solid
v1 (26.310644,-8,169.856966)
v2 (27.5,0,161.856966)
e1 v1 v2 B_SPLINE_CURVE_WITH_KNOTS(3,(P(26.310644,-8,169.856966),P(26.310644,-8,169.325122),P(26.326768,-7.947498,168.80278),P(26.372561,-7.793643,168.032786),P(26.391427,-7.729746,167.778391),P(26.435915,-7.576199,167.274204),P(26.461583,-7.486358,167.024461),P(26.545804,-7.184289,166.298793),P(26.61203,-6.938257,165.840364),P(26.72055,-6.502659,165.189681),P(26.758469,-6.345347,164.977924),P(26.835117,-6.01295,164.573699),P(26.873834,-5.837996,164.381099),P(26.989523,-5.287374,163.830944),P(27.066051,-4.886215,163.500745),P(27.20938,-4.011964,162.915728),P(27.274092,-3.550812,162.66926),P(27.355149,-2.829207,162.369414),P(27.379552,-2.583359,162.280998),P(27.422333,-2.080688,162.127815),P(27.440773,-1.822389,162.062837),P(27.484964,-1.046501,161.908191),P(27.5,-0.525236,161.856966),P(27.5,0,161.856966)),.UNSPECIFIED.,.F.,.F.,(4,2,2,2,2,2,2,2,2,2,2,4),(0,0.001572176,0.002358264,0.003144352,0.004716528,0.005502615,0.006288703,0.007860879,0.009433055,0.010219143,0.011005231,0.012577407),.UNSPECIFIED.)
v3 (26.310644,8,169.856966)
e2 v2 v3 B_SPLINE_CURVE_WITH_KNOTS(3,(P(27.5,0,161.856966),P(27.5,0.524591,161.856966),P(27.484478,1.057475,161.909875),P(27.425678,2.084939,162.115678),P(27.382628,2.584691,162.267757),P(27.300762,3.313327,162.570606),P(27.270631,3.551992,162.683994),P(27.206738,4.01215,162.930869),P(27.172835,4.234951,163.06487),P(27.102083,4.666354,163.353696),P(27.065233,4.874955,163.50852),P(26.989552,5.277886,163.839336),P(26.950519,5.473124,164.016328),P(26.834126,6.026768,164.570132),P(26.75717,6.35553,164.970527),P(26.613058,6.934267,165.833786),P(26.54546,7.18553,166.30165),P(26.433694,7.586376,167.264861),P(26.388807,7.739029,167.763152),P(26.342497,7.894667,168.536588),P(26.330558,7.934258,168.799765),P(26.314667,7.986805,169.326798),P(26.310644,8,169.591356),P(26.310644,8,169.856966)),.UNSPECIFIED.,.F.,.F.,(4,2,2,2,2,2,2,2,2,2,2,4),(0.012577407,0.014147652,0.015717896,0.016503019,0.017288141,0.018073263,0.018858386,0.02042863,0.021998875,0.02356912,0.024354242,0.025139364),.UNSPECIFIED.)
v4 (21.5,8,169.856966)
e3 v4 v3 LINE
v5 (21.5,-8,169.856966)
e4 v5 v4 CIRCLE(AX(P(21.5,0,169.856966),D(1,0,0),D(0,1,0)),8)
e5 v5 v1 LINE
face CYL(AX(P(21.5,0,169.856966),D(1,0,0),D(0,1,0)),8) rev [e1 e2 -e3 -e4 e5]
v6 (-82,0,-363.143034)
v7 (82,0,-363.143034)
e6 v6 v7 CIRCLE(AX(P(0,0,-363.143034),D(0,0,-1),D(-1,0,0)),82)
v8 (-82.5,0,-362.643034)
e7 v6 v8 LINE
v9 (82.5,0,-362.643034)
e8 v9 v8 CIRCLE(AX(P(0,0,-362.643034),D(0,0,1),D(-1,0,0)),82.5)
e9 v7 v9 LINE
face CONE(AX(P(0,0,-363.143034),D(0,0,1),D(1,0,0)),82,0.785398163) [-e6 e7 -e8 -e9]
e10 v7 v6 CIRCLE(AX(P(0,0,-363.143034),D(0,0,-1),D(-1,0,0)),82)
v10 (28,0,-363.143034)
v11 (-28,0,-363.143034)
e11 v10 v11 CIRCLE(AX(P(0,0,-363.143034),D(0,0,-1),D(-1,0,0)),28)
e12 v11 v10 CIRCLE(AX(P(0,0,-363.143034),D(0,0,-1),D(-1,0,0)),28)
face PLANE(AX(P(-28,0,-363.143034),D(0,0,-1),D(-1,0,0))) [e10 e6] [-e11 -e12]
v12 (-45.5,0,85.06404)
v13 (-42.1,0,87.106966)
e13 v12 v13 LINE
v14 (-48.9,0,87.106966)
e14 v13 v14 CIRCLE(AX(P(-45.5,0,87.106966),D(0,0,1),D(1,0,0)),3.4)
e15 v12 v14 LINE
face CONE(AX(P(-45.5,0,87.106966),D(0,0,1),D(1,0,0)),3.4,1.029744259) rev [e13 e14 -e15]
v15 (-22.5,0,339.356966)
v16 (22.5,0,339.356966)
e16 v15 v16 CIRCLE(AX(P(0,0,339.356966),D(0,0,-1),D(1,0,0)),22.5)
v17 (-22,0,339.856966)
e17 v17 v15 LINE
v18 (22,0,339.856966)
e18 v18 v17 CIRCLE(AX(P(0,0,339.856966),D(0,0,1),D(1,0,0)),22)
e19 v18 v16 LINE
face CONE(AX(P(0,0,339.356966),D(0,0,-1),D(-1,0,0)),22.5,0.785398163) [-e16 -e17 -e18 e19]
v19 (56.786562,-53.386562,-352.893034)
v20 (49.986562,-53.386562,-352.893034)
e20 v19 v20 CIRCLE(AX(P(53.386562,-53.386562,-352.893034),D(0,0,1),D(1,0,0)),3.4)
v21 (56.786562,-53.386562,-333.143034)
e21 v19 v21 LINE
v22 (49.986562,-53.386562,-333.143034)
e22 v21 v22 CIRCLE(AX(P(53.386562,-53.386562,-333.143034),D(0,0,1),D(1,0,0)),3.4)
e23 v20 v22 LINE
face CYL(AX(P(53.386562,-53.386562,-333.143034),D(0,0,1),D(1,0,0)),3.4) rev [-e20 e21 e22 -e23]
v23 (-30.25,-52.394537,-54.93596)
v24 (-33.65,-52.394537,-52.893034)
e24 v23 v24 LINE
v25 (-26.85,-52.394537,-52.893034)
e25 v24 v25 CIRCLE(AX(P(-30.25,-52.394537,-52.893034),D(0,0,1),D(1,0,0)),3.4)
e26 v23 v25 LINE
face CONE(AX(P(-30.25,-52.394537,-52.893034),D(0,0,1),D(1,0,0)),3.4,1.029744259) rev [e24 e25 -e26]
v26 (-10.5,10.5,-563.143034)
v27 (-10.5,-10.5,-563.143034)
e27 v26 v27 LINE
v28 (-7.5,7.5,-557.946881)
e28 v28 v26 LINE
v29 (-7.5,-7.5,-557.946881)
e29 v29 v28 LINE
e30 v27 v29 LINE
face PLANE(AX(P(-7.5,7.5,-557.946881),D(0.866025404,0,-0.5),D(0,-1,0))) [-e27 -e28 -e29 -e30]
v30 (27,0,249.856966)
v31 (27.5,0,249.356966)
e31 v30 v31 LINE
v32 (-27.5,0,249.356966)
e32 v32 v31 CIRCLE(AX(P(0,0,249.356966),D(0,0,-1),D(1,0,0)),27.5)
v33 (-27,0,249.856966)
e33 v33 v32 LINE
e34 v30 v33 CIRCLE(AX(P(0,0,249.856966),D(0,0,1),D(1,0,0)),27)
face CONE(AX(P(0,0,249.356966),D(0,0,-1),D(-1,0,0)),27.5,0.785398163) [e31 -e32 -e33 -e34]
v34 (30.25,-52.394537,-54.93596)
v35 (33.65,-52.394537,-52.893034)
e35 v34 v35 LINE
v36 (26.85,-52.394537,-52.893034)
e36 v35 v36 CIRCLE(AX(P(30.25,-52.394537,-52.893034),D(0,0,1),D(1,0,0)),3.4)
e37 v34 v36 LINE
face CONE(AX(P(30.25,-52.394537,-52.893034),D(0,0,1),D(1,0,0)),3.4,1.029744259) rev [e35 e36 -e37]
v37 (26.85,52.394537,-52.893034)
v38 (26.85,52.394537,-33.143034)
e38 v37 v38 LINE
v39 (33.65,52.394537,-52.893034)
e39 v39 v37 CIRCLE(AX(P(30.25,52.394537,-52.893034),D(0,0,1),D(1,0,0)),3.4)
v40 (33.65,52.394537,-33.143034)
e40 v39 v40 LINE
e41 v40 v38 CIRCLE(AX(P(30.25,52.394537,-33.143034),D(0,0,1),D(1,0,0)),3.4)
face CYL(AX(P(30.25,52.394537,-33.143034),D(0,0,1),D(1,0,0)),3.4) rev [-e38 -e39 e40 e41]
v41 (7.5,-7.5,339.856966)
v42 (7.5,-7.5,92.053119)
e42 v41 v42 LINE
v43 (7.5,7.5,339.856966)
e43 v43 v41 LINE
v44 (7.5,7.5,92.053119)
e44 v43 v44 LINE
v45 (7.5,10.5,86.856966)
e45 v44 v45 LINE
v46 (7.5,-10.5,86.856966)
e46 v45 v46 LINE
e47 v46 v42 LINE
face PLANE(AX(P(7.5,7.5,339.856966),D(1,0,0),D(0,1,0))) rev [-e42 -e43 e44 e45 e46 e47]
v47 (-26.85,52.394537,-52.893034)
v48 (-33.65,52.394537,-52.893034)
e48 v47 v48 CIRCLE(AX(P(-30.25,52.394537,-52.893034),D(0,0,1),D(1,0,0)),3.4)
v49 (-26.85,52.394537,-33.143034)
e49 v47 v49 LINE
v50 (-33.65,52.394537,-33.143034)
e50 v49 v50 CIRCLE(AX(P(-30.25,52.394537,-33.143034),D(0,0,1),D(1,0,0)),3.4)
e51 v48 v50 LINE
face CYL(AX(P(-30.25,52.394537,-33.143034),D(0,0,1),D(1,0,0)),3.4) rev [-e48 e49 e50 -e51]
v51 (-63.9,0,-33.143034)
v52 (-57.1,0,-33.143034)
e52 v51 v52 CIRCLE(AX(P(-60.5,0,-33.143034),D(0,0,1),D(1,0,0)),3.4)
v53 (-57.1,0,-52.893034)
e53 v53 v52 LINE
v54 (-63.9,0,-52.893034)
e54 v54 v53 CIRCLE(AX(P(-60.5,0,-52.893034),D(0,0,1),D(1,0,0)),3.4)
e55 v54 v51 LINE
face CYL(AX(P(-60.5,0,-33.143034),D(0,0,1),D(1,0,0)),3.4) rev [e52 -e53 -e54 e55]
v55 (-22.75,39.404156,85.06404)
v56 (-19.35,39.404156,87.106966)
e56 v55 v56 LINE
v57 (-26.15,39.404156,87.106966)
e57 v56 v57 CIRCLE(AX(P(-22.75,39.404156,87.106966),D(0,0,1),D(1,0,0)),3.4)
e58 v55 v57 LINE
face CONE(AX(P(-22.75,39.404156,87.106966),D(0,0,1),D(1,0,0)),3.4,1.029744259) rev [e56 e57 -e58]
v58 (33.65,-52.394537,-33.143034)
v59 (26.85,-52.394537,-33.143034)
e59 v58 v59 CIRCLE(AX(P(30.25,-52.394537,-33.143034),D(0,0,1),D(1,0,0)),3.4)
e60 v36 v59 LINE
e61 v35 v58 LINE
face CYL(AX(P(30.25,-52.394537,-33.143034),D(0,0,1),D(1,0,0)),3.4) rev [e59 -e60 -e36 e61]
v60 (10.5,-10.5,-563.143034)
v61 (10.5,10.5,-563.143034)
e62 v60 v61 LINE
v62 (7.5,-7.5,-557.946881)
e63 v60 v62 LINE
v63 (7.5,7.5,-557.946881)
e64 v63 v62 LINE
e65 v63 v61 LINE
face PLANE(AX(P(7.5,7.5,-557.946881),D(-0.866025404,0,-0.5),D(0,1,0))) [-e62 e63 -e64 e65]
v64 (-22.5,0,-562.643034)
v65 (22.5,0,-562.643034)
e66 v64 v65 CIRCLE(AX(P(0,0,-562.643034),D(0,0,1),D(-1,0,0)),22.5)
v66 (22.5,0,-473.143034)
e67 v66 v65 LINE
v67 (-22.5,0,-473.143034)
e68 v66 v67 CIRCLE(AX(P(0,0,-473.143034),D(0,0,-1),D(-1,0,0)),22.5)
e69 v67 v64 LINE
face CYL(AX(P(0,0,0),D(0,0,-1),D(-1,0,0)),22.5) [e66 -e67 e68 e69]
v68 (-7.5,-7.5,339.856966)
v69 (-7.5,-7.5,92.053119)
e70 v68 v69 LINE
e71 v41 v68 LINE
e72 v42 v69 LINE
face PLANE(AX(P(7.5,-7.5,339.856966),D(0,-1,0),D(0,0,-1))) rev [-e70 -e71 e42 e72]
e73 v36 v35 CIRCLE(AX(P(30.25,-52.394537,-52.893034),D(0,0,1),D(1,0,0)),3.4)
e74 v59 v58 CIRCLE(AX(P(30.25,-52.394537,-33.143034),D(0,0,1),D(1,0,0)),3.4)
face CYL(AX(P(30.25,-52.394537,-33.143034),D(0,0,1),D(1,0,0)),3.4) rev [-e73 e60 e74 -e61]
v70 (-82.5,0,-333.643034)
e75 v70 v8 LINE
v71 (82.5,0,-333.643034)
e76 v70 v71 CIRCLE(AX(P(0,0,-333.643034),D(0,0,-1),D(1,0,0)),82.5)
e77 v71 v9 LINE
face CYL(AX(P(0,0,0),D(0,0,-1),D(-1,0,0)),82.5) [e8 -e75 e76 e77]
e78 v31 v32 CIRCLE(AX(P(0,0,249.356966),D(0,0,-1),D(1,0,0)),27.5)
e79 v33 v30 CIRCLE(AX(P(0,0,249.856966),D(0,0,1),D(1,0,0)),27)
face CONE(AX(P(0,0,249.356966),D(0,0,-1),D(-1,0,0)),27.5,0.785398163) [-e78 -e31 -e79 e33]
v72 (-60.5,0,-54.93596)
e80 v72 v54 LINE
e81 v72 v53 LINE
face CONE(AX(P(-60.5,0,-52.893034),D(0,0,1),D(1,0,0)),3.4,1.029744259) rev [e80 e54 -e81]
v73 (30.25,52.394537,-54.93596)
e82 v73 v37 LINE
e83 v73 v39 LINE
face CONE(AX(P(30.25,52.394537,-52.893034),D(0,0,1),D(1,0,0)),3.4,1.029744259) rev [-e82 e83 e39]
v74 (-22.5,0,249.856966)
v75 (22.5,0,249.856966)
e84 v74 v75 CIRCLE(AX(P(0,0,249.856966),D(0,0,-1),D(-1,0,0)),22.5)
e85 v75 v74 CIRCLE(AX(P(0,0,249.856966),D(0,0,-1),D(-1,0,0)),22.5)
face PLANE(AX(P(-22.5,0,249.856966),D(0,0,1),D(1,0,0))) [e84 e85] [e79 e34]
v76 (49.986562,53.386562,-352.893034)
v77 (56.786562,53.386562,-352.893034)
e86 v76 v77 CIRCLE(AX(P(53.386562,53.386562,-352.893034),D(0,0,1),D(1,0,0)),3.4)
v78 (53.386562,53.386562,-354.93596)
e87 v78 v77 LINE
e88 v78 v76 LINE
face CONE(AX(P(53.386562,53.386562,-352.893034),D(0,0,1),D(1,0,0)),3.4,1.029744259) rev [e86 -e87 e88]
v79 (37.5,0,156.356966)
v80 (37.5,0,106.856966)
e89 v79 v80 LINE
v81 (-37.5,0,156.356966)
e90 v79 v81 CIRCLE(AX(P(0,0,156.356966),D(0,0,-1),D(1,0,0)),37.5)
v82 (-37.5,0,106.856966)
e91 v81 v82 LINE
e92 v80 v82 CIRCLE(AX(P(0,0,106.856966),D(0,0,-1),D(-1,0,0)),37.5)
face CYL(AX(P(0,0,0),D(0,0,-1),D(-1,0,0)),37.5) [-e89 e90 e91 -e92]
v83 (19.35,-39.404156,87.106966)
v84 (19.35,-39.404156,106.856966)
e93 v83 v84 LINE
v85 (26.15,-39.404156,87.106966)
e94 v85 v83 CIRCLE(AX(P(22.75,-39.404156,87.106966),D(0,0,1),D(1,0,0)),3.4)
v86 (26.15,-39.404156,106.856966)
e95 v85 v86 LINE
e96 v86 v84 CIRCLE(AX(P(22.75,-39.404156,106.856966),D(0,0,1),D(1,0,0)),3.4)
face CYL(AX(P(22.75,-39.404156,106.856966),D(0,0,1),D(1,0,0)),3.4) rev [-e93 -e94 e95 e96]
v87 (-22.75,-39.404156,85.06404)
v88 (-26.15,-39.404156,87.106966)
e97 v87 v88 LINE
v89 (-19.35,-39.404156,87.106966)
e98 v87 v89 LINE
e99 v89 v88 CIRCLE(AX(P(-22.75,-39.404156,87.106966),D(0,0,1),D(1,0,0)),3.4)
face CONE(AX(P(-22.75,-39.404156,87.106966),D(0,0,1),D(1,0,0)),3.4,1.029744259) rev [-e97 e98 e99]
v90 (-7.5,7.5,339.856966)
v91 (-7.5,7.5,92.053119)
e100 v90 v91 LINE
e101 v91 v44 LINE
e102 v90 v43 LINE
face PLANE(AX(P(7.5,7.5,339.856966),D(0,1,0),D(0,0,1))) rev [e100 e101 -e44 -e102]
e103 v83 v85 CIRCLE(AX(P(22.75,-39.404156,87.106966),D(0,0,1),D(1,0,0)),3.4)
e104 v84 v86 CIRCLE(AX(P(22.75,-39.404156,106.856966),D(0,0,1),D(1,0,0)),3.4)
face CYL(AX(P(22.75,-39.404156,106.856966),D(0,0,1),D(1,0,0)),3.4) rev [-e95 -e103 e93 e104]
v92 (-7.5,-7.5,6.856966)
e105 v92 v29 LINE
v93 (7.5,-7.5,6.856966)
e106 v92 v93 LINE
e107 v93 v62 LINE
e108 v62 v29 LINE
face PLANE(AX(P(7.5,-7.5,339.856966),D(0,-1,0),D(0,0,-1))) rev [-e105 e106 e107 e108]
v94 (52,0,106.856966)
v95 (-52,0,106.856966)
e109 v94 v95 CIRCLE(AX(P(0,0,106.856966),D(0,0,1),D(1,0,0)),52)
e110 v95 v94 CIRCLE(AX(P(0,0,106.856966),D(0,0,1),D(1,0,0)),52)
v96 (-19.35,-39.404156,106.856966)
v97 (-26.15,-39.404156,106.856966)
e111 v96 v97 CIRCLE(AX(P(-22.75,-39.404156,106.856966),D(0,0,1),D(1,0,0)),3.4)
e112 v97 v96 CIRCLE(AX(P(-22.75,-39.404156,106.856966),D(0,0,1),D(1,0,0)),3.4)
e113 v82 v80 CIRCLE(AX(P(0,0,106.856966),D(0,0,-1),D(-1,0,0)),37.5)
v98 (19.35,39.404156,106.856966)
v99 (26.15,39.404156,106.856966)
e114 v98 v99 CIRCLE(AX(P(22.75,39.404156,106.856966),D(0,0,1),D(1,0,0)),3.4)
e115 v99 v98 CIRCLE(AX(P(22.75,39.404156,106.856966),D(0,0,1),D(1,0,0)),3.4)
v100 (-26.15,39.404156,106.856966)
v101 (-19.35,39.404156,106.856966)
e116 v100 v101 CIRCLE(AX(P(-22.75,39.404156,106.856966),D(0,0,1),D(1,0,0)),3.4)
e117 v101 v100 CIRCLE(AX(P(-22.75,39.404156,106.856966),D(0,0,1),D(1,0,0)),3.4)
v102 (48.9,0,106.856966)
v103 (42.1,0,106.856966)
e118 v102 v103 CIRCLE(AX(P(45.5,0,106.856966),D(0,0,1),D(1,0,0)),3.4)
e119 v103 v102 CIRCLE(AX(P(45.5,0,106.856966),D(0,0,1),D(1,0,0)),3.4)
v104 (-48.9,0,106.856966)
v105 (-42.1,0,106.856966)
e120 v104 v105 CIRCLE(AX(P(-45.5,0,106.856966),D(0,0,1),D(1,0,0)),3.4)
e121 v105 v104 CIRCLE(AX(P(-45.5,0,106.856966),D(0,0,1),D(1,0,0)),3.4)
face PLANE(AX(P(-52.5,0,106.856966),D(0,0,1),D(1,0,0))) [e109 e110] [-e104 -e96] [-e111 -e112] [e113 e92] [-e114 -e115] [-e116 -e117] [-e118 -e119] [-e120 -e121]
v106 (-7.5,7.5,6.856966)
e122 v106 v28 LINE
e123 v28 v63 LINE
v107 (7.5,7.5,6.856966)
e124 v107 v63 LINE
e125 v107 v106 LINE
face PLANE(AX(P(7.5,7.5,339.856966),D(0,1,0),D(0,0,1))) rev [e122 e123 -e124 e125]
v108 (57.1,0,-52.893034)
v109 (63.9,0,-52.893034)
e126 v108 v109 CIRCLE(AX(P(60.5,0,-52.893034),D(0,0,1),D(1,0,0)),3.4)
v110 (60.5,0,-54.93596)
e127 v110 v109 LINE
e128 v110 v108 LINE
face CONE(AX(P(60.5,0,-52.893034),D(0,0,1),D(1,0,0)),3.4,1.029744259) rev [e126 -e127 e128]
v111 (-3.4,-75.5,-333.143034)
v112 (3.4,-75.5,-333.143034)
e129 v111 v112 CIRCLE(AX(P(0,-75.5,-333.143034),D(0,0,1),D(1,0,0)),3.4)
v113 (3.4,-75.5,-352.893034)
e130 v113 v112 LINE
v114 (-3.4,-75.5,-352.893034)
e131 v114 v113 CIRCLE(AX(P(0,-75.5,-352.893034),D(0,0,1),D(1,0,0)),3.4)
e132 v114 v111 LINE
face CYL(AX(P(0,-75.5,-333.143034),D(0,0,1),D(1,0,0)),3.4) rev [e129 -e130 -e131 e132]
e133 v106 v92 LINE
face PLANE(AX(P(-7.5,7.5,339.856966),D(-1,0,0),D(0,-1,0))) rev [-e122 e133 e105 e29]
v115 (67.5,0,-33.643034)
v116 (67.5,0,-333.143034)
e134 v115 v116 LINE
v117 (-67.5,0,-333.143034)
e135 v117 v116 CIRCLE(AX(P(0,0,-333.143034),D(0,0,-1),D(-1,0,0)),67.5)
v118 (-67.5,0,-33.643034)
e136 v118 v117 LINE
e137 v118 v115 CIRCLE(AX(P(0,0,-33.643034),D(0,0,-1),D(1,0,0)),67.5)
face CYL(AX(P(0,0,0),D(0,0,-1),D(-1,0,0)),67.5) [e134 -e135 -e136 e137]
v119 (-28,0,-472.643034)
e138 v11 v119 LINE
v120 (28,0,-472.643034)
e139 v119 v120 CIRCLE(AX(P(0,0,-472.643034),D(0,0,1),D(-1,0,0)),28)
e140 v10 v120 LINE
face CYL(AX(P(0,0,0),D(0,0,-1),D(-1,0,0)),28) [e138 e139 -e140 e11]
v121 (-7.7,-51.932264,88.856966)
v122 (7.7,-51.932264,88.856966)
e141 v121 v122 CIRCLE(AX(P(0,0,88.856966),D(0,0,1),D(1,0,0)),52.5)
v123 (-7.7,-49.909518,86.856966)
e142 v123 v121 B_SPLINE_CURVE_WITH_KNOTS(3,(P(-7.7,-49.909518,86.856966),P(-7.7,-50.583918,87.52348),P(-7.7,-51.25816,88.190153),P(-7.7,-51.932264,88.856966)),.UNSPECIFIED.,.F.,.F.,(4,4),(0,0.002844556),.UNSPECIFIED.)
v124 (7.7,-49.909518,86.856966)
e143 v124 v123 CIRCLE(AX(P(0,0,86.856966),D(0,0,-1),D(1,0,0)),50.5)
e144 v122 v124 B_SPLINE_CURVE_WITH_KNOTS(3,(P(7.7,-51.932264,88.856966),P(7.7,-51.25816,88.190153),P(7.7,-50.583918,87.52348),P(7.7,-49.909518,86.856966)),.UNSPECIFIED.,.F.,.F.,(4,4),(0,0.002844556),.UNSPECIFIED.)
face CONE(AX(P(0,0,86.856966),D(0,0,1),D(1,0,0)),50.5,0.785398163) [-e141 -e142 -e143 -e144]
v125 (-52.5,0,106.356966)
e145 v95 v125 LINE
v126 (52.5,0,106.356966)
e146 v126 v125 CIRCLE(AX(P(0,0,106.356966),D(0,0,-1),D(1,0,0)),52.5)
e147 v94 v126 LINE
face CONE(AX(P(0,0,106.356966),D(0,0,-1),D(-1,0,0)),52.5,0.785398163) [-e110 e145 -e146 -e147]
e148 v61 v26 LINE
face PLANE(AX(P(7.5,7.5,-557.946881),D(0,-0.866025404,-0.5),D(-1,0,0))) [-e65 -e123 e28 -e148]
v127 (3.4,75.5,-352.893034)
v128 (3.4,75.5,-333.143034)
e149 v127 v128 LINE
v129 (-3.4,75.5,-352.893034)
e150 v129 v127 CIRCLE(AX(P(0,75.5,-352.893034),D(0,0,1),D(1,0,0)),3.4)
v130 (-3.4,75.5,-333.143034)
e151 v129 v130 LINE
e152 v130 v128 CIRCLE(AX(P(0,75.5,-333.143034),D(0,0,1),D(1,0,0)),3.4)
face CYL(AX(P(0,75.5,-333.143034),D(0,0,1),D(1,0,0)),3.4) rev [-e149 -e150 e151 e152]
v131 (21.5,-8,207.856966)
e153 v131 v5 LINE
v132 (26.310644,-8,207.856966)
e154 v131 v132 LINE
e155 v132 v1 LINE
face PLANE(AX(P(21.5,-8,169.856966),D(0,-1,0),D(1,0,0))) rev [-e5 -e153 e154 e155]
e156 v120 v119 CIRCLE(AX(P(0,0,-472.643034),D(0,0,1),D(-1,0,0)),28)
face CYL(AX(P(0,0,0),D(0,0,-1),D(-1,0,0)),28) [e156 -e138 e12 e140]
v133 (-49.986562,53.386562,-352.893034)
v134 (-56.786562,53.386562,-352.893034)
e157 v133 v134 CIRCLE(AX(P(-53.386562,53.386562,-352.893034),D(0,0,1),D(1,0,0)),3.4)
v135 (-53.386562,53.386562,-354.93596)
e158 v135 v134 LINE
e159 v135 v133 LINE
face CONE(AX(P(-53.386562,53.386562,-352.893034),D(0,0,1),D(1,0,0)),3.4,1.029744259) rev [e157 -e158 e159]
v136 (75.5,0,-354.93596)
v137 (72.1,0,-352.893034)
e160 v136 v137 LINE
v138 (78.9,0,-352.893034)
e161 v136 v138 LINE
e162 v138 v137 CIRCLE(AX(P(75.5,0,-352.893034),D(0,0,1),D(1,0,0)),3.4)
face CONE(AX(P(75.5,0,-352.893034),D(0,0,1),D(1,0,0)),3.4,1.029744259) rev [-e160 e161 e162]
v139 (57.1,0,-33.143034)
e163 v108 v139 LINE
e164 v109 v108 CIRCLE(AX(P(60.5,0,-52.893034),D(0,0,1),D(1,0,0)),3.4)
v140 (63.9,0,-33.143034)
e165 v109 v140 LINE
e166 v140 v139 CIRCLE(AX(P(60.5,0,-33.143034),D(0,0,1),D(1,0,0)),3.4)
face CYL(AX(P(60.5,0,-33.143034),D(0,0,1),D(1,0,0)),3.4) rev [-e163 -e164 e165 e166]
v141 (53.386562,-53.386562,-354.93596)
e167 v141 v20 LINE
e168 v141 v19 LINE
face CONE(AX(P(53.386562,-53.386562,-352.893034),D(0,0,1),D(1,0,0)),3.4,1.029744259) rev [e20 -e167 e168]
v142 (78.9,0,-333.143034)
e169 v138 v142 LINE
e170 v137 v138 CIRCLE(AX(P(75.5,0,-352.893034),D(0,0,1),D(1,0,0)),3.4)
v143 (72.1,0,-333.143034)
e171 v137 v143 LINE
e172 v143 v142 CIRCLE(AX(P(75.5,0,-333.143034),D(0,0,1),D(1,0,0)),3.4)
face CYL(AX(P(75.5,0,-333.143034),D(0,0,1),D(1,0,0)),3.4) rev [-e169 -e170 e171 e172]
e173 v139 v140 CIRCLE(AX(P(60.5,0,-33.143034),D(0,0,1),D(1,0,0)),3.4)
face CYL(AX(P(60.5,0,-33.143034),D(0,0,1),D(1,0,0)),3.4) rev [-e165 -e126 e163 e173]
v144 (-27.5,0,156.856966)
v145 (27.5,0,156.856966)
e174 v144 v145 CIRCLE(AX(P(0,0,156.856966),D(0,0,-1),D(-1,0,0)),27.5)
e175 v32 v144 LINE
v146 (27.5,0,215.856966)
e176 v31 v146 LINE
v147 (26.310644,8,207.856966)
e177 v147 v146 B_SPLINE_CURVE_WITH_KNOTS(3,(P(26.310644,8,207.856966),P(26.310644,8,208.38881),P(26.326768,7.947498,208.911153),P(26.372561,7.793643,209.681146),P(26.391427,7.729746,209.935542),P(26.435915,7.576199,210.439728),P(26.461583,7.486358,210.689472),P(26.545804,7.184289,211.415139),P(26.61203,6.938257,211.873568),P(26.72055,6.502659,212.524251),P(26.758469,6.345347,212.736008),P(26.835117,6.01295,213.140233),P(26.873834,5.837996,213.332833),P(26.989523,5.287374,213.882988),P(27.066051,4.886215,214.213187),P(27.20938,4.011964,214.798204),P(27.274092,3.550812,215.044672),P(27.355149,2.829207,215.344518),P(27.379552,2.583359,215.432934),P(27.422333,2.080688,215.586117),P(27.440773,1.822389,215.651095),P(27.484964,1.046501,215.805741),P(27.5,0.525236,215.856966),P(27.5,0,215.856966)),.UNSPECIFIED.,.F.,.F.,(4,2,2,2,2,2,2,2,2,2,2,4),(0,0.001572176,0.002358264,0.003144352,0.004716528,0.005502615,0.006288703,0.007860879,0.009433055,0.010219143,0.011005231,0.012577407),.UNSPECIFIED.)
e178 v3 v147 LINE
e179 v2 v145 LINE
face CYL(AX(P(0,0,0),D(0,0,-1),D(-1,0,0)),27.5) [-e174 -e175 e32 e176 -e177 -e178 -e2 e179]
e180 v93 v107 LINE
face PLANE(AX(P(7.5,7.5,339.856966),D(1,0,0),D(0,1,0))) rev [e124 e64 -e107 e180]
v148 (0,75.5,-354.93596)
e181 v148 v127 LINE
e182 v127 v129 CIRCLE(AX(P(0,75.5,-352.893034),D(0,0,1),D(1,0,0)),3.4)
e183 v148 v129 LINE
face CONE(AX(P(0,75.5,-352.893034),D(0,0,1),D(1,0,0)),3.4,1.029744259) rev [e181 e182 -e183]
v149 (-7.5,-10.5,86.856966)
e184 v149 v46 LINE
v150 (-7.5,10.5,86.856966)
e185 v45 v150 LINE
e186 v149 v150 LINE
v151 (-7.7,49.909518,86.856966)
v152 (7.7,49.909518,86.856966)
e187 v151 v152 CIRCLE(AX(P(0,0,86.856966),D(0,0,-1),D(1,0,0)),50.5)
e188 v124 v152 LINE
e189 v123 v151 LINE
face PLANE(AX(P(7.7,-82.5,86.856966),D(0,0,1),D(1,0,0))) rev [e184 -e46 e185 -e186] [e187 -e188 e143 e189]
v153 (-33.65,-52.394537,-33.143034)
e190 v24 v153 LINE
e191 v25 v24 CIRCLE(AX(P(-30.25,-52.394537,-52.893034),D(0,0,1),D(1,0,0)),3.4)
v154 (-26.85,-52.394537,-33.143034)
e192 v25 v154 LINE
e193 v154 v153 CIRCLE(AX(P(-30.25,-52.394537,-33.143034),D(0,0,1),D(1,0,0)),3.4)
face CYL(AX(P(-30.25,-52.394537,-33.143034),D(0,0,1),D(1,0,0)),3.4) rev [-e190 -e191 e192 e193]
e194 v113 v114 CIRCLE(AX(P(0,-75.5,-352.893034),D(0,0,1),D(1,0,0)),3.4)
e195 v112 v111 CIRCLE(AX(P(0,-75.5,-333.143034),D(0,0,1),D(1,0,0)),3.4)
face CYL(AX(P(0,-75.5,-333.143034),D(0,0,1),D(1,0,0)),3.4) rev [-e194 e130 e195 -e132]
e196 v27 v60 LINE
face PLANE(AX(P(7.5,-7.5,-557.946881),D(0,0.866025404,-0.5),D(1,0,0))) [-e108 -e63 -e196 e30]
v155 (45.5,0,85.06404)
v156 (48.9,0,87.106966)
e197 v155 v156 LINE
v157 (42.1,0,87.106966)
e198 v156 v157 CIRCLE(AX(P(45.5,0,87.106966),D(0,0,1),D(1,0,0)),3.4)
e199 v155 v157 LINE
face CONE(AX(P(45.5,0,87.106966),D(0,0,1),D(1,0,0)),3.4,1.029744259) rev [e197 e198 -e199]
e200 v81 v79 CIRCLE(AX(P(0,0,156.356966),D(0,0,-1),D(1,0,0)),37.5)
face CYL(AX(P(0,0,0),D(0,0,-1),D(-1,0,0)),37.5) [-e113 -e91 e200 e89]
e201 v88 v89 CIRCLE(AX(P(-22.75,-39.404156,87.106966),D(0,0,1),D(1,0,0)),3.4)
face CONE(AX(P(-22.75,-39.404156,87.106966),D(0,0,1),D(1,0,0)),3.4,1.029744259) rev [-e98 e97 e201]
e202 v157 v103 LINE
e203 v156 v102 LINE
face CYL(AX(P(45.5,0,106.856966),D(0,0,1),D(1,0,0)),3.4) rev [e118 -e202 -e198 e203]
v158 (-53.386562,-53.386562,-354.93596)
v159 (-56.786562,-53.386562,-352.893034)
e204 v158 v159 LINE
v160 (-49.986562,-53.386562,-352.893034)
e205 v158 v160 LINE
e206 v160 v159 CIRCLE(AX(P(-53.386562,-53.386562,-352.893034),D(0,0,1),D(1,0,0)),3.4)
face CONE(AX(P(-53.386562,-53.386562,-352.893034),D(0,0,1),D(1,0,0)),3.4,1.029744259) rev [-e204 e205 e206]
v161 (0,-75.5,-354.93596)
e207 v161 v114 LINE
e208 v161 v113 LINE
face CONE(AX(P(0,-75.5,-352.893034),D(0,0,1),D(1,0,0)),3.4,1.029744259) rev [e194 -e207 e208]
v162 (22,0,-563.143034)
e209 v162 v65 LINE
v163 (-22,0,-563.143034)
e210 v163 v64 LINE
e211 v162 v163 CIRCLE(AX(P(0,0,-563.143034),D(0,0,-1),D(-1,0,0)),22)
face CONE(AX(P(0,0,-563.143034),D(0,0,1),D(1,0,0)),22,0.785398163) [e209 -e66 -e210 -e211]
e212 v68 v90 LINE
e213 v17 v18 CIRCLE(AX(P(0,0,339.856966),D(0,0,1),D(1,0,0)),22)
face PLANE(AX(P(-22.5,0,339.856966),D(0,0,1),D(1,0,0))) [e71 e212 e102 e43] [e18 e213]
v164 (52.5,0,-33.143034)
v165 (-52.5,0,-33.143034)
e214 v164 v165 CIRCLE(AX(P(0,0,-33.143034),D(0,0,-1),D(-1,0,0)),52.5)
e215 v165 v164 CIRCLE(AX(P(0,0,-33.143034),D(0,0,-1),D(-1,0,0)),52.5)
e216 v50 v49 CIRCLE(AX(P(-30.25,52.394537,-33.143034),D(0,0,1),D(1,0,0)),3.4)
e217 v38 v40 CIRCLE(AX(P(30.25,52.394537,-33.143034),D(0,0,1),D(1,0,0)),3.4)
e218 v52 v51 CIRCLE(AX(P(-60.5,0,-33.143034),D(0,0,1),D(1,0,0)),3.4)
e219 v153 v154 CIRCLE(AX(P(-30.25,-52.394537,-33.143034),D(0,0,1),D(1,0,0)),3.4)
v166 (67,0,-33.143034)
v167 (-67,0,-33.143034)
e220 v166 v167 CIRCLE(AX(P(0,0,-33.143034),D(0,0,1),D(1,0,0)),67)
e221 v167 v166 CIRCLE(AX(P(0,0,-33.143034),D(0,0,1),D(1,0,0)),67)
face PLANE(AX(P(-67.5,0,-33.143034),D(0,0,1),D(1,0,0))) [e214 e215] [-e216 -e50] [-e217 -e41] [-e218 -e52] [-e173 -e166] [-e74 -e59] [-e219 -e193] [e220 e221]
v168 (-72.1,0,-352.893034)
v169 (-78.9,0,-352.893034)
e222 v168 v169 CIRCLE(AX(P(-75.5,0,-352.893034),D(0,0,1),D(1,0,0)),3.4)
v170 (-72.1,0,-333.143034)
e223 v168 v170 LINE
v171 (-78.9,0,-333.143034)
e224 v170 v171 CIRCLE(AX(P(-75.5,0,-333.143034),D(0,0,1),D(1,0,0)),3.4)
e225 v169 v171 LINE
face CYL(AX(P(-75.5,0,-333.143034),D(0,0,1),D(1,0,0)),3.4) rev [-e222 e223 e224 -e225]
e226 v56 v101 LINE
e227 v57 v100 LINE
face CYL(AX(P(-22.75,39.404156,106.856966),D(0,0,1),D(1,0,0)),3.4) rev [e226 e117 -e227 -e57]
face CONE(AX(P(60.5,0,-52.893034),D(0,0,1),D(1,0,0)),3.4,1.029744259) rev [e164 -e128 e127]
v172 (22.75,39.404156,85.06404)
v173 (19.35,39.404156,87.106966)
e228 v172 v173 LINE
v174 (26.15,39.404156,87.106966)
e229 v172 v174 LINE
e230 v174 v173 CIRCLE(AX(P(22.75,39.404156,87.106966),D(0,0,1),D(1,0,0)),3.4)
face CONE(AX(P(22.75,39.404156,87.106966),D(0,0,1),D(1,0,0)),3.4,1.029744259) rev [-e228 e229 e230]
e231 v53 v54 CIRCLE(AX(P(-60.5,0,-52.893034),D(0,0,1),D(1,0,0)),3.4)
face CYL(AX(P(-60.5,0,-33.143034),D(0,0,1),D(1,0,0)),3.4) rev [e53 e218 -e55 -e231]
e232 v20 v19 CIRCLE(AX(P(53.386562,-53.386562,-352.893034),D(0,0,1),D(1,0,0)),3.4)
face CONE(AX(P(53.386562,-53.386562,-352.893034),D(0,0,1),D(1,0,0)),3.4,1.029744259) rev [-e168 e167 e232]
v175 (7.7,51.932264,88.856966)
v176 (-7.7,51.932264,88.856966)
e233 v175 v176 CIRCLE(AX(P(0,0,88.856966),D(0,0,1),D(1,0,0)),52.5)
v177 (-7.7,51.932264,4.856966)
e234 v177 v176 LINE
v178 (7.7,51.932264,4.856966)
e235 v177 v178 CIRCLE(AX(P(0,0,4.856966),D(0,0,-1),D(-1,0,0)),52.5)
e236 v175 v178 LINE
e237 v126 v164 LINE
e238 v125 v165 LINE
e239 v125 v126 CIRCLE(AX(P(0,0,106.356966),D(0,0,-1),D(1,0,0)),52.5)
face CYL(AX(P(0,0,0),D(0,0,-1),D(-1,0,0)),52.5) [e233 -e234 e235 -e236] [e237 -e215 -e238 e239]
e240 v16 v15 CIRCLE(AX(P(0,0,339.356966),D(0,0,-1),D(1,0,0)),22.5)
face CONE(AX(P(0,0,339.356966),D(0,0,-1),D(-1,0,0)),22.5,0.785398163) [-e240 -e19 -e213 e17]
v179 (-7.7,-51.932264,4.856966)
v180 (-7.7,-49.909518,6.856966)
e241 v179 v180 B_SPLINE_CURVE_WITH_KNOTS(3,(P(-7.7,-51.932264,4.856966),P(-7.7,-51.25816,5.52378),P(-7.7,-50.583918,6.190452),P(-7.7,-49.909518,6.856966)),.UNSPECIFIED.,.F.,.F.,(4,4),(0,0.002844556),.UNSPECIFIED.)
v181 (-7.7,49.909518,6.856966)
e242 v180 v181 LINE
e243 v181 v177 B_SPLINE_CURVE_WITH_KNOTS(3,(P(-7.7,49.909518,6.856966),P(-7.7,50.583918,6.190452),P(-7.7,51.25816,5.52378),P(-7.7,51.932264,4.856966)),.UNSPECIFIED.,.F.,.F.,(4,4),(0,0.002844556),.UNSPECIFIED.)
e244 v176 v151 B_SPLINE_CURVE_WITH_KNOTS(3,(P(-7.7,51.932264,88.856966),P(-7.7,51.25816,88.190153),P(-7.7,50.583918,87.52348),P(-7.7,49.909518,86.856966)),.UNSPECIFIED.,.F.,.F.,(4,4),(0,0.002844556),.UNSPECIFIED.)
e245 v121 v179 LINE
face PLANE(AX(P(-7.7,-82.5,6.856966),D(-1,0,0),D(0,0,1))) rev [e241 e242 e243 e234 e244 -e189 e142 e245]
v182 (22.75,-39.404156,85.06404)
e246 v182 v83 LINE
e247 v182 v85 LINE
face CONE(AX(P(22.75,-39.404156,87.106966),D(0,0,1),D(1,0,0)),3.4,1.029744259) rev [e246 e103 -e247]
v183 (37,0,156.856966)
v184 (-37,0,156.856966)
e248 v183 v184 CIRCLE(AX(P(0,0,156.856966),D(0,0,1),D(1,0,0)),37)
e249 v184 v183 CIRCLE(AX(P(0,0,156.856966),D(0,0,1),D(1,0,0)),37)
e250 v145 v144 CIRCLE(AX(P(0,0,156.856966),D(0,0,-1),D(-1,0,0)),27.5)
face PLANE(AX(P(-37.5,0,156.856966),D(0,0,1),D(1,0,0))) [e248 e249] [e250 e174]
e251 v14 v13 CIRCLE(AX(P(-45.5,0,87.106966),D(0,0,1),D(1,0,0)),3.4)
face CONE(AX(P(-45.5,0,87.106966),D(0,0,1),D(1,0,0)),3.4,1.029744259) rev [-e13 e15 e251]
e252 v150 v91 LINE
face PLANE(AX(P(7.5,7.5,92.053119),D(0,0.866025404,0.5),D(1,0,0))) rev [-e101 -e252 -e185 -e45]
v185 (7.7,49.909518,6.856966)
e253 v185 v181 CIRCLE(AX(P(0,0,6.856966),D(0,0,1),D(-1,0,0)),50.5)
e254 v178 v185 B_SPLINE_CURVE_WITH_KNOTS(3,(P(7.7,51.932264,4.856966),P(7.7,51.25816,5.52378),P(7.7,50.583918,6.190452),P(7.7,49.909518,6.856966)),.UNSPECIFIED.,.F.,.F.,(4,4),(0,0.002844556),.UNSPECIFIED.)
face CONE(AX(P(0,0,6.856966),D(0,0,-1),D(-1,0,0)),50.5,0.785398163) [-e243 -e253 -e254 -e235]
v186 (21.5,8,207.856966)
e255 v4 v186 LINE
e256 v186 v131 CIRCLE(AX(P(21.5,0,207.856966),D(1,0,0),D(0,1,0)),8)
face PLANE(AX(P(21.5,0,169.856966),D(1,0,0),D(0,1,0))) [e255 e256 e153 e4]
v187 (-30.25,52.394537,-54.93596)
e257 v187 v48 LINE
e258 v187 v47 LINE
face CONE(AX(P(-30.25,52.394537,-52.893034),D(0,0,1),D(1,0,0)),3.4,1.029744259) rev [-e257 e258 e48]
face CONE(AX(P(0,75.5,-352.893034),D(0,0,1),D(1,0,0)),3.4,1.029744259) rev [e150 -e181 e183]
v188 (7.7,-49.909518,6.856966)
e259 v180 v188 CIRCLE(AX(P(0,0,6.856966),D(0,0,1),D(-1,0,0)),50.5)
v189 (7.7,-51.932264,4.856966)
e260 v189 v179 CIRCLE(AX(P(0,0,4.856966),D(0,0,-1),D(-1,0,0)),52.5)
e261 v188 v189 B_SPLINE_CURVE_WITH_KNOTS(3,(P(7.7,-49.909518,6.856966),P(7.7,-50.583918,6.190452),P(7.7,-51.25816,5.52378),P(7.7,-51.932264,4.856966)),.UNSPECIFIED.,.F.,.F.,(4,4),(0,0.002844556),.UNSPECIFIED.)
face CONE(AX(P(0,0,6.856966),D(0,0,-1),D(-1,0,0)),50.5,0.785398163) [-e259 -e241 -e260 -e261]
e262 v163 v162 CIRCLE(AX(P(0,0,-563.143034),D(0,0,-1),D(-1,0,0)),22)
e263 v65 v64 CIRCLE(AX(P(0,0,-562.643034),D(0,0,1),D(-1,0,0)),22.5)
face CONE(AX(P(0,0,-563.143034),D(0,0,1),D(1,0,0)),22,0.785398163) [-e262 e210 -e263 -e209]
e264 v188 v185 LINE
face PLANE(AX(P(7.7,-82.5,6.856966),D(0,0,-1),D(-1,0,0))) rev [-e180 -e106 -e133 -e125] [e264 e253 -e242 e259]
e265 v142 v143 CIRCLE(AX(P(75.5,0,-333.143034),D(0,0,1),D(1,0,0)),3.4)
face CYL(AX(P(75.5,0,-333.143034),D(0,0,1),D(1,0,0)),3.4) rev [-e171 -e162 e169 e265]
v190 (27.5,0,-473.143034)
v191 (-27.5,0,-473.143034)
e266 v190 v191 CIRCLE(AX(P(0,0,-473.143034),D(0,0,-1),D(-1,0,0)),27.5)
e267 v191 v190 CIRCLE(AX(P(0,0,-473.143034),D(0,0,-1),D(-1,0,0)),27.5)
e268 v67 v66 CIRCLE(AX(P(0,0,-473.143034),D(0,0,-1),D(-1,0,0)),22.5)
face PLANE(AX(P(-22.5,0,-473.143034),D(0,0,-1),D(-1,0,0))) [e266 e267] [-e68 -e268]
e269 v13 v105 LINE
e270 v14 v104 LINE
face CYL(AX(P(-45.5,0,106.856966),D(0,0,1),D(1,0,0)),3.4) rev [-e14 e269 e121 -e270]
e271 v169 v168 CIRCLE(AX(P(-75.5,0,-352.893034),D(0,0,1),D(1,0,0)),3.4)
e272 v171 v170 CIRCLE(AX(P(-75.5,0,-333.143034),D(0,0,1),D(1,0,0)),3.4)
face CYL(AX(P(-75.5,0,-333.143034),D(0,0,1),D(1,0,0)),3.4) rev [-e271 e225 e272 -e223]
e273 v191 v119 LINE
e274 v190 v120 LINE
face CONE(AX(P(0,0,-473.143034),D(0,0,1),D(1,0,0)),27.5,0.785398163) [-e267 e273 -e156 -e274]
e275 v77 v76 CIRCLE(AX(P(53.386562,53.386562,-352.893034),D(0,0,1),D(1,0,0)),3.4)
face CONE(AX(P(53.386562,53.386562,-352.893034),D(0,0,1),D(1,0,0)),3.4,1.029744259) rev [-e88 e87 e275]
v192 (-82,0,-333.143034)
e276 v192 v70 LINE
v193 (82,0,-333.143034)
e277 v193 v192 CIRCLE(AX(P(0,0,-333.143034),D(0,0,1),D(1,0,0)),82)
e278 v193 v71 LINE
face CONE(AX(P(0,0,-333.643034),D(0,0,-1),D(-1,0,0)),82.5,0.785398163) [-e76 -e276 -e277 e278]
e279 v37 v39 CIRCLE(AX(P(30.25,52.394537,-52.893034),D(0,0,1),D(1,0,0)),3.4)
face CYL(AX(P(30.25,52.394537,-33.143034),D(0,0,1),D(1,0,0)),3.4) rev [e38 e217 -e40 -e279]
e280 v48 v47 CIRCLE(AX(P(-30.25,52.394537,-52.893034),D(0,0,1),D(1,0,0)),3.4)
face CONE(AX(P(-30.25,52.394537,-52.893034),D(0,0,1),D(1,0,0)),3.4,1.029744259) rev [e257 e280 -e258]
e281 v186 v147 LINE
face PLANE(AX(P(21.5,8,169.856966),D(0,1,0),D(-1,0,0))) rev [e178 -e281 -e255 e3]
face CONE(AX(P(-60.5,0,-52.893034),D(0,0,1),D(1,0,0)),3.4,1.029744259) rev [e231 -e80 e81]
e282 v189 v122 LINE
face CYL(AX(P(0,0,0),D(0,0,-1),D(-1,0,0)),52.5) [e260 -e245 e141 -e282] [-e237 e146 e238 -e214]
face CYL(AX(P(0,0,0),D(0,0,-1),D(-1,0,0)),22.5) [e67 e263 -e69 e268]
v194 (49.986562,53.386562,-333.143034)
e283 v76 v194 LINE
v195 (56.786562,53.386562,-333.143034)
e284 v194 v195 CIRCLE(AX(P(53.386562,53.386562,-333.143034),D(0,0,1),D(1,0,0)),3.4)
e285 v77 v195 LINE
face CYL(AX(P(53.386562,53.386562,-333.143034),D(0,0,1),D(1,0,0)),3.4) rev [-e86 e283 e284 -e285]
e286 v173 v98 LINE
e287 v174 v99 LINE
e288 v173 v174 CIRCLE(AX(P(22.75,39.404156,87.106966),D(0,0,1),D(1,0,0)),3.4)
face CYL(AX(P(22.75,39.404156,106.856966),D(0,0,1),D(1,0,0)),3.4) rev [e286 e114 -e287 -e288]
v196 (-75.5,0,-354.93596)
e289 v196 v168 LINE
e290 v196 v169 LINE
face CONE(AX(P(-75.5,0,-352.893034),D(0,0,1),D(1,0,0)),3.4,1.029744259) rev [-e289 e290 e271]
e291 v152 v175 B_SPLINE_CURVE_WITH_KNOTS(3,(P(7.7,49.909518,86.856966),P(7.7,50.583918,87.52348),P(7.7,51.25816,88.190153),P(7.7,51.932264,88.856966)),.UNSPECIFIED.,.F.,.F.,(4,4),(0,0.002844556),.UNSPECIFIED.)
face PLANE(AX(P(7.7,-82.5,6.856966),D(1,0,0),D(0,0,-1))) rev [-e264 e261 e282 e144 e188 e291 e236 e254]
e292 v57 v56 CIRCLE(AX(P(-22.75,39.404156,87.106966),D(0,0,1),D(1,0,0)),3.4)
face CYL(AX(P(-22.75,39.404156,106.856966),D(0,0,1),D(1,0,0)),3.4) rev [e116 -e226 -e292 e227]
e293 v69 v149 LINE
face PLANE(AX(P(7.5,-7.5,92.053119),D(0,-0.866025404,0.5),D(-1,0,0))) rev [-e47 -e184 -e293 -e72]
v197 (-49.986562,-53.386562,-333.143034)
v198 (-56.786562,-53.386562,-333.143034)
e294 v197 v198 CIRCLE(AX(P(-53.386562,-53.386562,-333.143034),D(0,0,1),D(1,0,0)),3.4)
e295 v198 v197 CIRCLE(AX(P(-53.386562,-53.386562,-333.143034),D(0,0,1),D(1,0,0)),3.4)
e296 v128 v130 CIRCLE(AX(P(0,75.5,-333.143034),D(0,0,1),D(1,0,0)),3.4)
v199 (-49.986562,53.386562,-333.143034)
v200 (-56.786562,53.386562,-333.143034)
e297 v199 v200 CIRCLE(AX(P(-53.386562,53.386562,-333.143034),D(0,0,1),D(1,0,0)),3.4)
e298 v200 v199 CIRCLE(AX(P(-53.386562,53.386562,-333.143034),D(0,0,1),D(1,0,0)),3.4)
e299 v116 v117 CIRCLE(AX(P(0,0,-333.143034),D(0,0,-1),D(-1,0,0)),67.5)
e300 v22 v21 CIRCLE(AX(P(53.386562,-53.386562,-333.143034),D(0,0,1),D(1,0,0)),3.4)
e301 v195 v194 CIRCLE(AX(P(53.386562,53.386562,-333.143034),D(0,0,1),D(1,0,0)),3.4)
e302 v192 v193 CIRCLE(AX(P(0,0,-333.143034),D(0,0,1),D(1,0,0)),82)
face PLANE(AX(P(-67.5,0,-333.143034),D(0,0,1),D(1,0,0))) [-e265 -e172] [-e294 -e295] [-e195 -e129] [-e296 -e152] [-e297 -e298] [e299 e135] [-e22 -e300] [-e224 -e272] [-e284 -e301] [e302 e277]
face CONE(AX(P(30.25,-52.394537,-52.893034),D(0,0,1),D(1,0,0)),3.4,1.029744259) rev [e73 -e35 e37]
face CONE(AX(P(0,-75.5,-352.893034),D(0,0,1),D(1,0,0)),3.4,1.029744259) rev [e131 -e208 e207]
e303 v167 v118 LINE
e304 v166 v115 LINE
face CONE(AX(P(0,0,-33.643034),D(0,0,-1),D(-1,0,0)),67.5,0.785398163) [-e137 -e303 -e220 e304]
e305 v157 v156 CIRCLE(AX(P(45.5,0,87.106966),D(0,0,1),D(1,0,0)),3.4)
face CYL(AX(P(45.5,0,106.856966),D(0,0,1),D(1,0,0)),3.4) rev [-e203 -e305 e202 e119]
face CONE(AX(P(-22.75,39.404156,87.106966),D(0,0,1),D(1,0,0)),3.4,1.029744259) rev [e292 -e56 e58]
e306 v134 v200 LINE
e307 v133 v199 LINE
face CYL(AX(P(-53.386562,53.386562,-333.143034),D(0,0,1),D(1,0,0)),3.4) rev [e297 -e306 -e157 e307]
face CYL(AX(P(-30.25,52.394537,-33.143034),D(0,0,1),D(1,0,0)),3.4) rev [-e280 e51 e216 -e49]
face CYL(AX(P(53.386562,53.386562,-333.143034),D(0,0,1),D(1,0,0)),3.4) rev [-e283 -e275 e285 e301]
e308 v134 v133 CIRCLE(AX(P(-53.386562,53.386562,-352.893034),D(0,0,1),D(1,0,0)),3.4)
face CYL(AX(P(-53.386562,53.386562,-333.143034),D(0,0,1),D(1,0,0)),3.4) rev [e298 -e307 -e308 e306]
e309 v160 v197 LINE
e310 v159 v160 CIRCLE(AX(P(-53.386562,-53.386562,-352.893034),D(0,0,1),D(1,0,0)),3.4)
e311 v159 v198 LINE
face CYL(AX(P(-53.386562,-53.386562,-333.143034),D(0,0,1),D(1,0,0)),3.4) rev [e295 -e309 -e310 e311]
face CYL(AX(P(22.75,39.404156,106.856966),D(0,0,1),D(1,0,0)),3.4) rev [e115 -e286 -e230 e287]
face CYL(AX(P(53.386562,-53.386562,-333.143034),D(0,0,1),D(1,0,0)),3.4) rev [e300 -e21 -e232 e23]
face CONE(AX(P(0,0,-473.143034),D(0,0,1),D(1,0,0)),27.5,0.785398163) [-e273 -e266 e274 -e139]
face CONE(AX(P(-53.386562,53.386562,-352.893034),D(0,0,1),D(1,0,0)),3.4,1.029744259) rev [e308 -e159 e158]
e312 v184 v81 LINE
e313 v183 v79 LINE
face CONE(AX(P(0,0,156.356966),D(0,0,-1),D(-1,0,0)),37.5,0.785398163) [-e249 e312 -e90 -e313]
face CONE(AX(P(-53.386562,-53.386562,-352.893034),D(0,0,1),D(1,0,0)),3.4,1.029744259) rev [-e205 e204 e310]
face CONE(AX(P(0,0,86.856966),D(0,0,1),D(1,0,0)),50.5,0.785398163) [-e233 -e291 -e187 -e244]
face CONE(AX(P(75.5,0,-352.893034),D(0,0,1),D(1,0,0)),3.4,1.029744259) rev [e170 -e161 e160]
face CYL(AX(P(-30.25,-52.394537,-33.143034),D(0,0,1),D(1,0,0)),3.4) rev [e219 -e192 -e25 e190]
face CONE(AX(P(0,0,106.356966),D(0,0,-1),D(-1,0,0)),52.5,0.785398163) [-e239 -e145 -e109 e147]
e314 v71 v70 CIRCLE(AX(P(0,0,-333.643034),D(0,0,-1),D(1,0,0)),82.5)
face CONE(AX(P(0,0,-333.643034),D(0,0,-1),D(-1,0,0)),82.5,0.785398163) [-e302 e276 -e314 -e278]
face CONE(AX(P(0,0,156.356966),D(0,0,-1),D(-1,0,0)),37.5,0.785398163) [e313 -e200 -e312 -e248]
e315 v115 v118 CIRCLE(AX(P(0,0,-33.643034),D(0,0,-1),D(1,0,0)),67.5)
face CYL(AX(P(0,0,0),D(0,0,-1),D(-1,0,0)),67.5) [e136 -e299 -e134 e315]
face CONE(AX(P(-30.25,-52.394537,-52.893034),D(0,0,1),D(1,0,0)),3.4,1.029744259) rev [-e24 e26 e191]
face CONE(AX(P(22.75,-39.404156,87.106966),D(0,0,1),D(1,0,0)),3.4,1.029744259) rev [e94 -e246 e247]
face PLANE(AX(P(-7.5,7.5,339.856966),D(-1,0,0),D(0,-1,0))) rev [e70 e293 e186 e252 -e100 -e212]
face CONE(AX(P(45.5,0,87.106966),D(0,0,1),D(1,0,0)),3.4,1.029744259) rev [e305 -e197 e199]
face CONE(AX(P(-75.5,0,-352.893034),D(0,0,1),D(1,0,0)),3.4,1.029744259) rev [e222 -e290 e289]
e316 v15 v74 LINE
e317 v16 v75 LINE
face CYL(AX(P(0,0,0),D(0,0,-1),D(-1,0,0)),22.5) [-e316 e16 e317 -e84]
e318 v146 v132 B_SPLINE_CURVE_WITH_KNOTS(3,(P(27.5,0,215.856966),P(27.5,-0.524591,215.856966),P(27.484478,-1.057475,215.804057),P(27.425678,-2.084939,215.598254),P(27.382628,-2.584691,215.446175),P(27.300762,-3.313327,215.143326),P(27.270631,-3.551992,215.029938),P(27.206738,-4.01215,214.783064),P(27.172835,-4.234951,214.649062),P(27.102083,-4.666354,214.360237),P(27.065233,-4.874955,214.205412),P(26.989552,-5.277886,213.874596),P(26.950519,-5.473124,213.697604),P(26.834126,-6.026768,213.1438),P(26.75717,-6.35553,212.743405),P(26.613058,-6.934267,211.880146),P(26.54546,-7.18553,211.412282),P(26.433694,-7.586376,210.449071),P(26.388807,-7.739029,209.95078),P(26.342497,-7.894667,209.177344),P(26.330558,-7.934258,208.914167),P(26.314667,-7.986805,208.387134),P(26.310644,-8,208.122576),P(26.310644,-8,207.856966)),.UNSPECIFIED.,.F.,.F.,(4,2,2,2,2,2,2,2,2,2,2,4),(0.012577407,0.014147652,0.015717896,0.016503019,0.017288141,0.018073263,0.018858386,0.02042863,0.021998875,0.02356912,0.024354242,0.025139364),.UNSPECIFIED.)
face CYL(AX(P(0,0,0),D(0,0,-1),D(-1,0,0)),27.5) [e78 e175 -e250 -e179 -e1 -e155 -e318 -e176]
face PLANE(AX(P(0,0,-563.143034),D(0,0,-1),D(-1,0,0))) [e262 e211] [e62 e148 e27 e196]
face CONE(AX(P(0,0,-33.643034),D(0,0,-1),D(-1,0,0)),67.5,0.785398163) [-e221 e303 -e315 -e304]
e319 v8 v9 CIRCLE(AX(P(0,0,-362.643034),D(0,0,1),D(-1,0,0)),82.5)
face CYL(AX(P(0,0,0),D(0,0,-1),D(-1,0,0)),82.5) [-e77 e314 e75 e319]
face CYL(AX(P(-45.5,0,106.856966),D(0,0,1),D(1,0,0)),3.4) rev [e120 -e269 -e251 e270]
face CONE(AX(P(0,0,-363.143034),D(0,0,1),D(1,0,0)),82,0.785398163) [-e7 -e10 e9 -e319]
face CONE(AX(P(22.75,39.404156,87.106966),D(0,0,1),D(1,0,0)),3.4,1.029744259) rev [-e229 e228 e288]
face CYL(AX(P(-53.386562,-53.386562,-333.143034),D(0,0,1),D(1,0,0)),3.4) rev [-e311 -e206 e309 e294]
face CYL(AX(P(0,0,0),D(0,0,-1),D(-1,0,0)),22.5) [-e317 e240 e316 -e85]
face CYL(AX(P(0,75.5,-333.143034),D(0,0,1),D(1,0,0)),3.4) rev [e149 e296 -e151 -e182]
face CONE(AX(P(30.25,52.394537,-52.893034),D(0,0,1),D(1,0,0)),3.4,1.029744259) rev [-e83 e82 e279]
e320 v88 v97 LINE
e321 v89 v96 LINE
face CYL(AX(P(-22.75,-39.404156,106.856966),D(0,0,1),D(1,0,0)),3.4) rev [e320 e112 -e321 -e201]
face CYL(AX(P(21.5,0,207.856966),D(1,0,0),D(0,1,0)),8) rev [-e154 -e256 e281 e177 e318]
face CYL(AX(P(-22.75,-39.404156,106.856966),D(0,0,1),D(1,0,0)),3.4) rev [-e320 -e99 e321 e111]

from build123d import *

# Parameters (mm, degrees)
SKETCH_3_W               = 15
SKETCH_3_H               = 15
CUT_EXTRUDE_1_DEPTH      = 911.506177903
CUT_EXTRUDE_2_DEPTH      = 576.102231468
CUT_EXTRUDE_2_DEPTH_BACK = 576.102231468
SKETCH_4_W               = 15.4
SKETCH_4_H               = 80
CHAMFER_1_SIZE           = 2
PATTERN_CIRCULAR_1_COUNT = 6
PATTERN_CIRCULAR_2_COUNT = 6
PATTERN_CIRCULAR_3_COUNT = 8
CHAMFER_2_SIZE           = 0.5
CHAMFER_3_SIZE           = 3
CHAMFER_3_SIZE2          = 5.196152423
CHAMFER_4_SIZE           = 3
CHAMFER_4_SIZE2          = 5.196152423
CUT_EXTRUDE_3_DEPTH      = 6


with BuildPart() as part:
    # 草图2 → 旋转1 (revolve)
    with BuildSketch(Plane(origin=(0, 0, 0), x_dir=(1, 0, 0), z_dir=(0, 1, 0))):
        Polygon((0, 563.143033908), (-22.5, 563.143033908), (-22.5, 473.143033908), (-28, 473.143033908), (-28, 363.143033908), (-82.5, 363.143033908), (-82.5, 333.143033908), (-67.5, 333.143033908), (-67.5, 33.143033908), (-52.5, 33.143033908), (-52.5, -106.856966092), (-37.5, -106.856966092), (-37.5, -156.856966092), (-27.5, -156.856966092), (-27.5, -249.856966092), (-22.5, -249.856966092), (-22.5, -339.856966092), (0, -339.856966092), align=None)
    revolve(axis=Axis((0, 0, 0), (0, 0, 1)))

    # 草图3 → 切除-拉伸1 (cut, through all)
    with BuildSketch(Plane(origin=(0, 0, -563.143033908), x_dir=(-1, 0, 0), z_dir=(0, 0, -1))):
        Rectangle(SKETCH_3_W, SKETCH_3_H)
    extrude(amount=-CUT_EXTRUDE_1_DEPTH, mode=Mode.SUBTRACT)

    # 草图4 → 切除-拉伸2 (cut, two sides: drawn at the far end of the back side and taken through both)
    with BuildSketch(Plane(origin=(0, 0, 0), x_dir=(1, 0, 0), z_dir=(0, 1, 0)).offset(-CUT_EXTRUDE_2_DEPTH_BACK)):
        with Locations((0, -46.856966092)):
            Rectangle(SKETCH_4_W, SKETCH_4_H)
    extrude(amount=CUT_EXTRUDE_2_DEPTH + CUT_EXTRUDE_2_DEPTH_BACK, mode=Mode.SUBTRACT)

    # 倒角1
    chamfer_1_edges = [part.edges().sort_by_distance(p)[0] for p in [
        (0, -52.5, 86.856966092),
        (0, 52.5, 86.856966092),
        (0, -52.5, 6.856966092),
        (0, 52.5, 6.856966092),
    ]]
    chamfer(chamfer_1_edges, length=CHAMFER_1_SIZE)

    # 草图6 → M8 螺纹孔1 (revolve, cut)
    with BuildSketch(Plane(origin=(-45.5, 0, 106.856966092), x_dir=(0, -1, 0), z_dir=(1, 0, 0))):
        Polygon((0, 0), (0, 21.792926105), (3.4, 19.75), (3.4, 0), align=None)
    hole_wizard_m8_1 = revolve(axis=Axis((-45.5, 0, 113.206966092), (0, 0, -1)), mode=Mode.SUBTRACT)

    # 阵列(圆周)1: M8 螺纹孔1 ×6 about axis
    pattern_circular_1_axis = Axis((0, 0, 0), (0, 0, 1))
    for i in range(1, PATTERN_CIRCULAR_1_COUNT):
        add(hole_wizard_m8_1.rotate(pattern_circular_1_axis, i * 360 / PATTERN_CIRCULAR_1_COUNT), mode=Mode.SUBTRACT)

    # 草图9 → M8 螺纹孔2 (revolve, cut)
    with BuildSketch(Plane(origin=(60.5, 0, -33.143033908), x_dir=(0, -1, 0), z_dir=(1, 0, 0))):
        Polygon((0, 0), (0, 21.792926105), (3.4, 19.75), (3.4, 0), align=None)
    hole_wizard_m8_2 = revolve(axis=Axis((60.5, 0, -26.793033908), (0, 0, -1)), mode=Mode.SUBTRACT)

    # 阵列(圆周)2: M8 螺纹孔2 ×6 about axis
    pattern_circular_2_axis = Axis((0, 0, 0), (0, 0, 1))
    for i in range(1, PATTERN_CIRCULAR_2_COUNT):
        add(hole_wizard_m8_2.rotate(pattern_circular_2_axis, i * 360 / PATTERN_CIRCULAR_2_COUNT), mode=Mode.SUBTRACT)

    # 草图11 → M8 螺纹孔3 (revolve, cut)
    with BuildSketch(Plane(origin=(-75.5, 0, -333.143033908), x_dir=(0, -1, 0), z_dir=(1, 0, 0))):
        Polygon((0, 0), (0, 21.792926105), (3.4, 19.75), (3.4, 0), align=None)
    hole_wizard_m8_3 = revolve(axis=Axis((-75.5, 0, -326.793033908), (0, 0, -1)), mode=Mode.SUBTRACT)

    # 阵列(圆周)3: M8 螺纹孔3 ×8 about axis
    pattern_circular_3_axis = Axis((0, 0, 0), (0, 0, 1))
    for i in range(1, PATTERN_CIRCULAR_3_COUNT):
        add(hole_wizard_m8_3.rotate(pattern_circular_3_axis, i * 360 / PATTERN_CIRCULAR_3_COUNT), mode=Mode.SUBTRACT)

    # 倒角2
    chamfer_2_edges = [part.edges().sort_by_distance(p)[0] for p in [
        (22.5, 0, 339.856966092),
        (27.5, 0, 249.856966092),
        (37.5, 0, 156.856966092),
        (52.5, 0, 106.856966092),
        (67.5, 0, -33.143033908),
        (82.5, 0, -333.143033908),
        (82.5, 0, -363.143033908),
        (28, 0, -473.143033908),
        (22.5, 0, -563.143033908),
    ]]
    chamfer(chamfer_2_edges, length=CHAMFER_2_SIZE)

    # 倒角3
    chamfer_3_edges = [part.edges().sort_by_distance(p)[0] for p in [
        (-7.5, 0, -563.143033908),
        (0, 7.5, -563.143033908),
        (7.5, 0, -563.143033908),
        (0, -7.5, -563.143033908),
    ]]
    chamfer_3_side = [part.faces().sort_by_distance(p)[0] for p in [
        (21.377746033, 0, -563.143033908),
    ]]
    chamfer(chamfer_3_edges, length=CHAMFER_3_SIZE, length2=CHAMFER_3_SIZE2, reference=chamfer_3_side[0])

    # 倒角4
    chamfer_4_edges = [part.edges().sort_by_distance(p)[0] for p in [
        (0, 7.5, 86.856966092),
        (0, -7.5, 86.856966092),
    ]]
    chamfer_4_side = [part.faces().sort_by_distance(p)[0] for p in [
        (-7.597832686, 0, 86.856966092),
    ]]
    chamfer(chamfer_4_edges, length=CHAMFER_4_SIZE, length2=CHAMFER_4_SIZE2, reference=chamfer_4_side[0])

    # 草图12 → 切除-拉伸3 (cut)
    with BuildSketch(Plane(origin=(27.5, 0, 0), x_dir=(0, 0, -1), z_dir=(1, 0, 0))):
        with BuildLine():
            Line((-169.856966092, -8), (-207.856966092, -8))
            ThreePointArc((-207.856966092, -8), (-215.856966092, 0), (-207.856966092, 8))
            Line((-207.856966092, 8), (-169.856966092, 8))
            ThreePointArc((-169.856966092, 8), (-161.856966092, 0), (-169.856966092, -8))
        make_face()
    extrude(amount=-CUT_EXTRUDE_3_DEPTH, mode=Mode.SUBTRACT)


solid = part.part
